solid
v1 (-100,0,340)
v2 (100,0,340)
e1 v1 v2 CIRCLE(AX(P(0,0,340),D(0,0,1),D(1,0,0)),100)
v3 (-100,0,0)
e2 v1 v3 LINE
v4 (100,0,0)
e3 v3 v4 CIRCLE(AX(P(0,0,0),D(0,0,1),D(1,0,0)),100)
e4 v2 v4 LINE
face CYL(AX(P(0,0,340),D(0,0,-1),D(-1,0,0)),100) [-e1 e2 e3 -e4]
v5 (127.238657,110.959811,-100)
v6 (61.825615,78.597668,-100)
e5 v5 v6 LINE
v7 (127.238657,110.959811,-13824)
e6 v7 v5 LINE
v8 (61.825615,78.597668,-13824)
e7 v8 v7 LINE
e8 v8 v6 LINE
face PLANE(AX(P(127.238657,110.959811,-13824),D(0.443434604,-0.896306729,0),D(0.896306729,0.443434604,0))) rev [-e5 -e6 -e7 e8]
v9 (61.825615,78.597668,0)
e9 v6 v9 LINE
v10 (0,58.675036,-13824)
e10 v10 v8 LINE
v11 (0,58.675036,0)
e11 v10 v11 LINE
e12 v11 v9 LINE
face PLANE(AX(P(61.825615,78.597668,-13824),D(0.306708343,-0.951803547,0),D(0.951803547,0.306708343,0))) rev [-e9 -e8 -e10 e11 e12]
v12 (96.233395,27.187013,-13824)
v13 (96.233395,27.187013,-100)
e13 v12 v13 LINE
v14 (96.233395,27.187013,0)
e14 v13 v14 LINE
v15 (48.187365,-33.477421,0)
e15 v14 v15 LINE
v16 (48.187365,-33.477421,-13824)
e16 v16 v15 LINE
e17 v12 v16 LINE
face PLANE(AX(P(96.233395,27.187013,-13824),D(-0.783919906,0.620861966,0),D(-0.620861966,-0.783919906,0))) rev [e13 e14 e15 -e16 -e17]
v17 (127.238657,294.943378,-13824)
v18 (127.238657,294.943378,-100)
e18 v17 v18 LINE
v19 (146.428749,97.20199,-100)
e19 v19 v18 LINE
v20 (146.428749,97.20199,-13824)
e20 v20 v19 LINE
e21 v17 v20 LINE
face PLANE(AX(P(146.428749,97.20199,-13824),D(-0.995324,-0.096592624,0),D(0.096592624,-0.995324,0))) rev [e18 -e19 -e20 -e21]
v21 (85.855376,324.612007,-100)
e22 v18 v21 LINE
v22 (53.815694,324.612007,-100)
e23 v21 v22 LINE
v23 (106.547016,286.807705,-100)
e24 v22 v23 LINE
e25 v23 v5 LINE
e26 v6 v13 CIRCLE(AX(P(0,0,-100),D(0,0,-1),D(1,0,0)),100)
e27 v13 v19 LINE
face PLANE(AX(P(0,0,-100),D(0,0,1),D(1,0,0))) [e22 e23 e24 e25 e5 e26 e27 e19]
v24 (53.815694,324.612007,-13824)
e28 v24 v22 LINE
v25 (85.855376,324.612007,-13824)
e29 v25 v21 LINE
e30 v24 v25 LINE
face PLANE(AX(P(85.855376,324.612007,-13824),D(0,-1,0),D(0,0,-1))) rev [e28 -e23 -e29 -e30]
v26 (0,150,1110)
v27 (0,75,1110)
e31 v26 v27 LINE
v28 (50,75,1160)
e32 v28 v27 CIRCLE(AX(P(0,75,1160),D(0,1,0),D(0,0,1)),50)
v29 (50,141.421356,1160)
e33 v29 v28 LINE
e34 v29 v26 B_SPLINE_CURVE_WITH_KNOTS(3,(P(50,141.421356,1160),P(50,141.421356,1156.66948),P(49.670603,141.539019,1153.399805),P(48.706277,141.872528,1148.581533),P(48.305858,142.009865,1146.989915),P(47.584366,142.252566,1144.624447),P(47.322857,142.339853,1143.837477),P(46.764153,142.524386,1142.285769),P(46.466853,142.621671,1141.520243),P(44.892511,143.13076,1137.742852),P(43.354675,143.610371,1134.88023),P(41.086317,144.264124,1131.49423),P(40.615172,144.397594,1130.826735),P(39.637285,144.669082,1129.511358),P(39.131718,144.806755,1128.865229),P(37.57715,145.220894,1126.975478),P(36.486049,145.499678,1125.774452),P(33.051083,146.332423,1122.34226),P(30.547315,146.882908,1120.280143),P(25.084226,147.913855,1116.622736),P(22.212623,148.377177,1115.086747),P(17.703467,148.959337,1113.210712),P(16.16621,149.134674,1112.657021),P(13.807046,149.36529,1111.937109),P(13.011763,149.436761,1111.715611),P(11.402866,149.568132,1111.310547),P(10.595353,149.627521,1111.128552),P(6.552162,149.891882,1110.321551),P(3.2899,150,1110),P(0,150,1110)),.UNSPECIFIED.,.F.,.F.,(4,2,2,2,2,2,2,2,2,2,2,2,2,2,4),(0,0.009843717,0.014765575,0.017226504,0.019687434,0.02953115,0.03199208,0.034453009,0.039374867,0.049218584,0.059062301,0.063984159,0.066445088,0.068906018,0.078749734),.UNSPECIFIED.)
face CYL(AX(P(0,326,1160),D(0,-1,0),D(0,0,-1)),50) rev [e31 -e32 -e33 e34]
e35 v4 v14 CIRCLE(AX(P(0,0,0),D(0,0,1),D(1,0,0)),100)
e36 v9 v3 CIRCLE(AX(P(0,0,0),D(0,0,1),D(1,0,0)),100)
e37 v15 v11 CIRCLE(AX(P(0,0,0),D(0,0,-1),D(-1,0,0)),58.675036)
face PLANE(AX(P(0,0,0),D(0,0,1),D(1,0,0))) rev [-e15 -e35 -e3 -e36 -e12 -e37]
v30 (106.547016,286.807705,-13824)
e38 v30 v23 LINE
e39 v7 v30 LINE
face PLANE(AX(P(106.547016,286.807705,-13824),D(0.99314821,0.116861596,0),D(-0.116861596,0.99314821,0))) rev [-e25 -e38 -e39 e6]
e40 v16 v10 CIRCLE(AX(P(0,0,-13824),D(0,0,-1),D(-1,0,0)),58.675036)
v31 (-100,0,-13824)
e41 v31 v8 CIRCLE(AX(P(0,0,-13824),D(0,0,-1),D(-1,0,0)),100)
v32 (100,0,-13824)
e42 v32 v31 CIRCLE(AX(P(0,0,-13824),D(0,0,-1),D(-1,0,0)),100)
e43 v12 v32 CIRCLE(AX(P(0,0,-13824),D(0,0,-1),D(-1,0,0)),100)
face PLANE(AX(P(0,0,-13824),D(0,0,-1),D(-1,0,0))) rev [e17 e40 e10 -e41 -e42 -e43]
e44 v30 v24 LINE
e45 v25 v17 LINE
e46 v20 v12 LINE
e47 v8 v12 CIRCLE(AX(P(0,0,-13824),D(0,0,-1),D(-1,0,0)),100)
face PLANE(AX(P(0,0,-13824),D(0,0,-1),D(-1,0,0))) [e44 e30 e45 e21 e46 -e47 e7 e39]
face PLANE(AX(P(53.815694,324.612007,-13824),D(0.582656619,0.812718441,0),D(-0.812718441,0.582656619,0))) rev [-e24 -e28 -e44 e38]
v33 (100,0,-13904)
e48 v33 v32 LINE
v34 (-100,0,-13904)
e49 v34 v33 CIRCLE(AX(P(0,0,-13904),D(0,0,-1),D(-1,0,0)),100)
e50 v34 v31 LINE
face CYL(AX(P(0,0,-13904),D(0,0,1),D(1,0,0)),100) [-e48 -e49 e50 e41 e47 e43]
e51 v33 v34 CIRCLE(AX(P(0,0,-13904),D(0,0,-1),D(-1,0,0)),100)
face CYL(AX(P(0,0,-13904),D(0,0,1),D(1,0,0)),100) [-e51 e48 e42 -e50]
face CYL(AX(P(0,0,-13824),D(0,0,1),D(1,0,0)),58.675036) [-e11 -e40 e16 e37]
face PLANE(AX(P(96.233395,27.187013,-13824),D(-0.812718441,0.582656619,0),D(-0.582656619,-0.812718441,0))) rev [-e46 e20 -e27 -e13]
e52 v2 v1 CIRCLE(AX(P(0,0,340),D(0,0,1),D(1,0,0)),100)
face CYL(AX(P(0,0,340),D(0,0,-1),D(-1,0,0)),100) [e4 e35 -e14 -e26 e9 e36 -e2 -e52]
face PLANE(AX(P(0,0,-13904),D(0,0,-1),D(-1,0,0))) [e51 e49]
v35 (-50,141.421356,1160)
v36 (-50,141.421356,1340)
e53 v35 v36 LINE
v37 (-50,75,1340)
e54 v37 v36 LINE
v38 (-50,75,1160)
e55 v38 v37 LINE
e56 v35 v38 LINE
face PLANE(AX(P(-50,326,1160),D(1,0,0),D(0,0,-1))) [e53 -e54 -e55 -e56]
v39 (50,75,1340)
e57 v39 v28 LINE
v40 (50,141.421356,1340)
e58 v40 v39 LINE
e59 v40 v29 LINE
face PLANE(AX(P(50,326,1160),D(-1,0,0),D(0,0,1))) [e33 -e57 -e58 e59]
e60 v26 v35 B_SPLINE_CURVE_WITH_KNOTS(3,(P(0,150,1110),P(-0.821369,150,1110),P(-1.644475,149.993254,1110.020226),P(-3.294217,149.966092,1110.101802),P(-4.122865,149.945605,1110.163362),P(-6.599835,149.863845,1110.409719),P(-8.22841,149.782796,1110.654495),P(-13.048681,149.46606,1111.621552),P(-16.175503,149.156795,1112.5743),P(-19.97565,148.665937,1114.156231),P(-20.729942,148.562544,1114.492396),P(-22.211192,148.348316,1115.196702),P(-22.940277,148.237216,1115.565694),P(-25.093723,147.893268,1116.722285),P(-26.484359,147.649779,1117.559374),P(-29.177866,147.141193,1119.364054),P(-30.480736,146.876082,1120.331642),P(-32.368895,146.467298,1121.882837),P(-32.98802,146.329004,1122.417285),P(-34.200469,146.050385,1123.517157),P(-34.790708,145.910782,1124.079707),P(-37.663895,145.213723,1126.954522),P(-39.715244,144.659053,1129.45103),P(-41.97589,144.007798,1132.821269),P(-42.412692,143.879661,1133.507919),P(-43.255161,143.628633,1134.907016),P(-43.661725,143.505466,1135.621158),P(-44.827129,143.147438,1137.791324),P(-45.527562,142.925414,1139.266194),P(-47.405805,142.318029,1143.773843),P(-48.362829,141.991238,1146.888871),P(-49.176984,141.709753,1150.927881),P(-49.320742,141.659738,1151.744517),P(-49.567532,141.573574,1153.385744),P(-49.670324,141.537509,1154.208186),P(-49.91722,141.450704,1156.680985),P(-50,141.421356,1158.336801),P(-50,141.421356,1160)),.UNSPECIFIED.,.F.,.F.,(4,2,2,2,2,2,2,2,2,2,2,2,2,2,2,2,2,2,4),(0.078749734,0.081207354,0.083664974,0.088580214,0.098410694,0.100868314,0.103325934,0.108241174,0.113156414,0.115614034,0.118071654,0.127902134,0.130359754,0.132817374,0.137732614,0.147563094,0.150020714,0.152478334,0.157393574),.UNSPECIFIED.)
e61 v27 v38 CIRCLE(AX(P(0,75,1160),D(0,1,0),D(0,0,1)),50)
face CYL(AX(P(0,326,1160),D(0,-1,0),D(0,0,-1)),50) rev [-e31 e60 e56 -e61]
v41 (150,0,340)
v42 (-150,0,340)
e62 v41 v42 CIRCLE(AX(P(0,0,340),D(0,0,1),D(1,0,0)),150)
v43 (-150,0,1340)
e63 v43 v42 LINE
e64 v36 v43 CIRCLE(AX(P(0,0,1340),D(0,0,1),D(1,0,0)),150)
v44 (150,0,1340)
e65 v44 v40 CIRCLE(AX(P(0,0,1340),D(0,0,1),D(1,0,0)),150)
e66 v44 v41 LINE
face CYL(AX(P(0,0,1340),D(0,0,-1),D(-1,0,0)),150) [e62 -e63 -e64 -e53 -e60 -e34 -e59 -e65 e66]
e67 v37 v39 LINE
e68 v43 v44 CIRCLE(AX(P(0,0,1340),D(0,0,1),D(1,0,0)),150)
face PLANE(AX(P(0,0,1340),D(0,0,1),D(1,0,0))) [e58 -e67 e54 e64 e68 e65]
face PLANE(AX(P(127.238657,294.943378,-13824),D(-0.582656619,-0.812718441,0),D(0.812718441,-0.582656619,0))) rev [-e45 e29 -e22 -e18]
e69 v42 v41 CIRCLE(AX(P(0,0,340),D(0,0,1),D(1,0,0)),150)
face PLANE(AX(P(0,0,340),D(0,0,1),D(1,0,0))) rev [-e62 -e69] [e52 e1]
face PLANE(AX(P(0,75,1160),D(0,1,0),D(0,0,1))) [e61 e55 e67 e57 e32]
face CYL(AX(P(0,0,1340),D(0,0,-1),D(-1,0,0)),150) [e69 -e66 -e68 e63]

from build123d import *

# Parameters (mm, degrees)
SKETCH1_R           = 100
BOSS_EXTRUDE1_DEPTH = 340
BOSS_EXTRUDE2_DEPTH = 13824
BOSS_EXTRUDE3_START = 80
SKETCH3_R           = 100
BOSS_EXTRUDE3_DEPTH = 80
CUT_EXTRUDE1_START  = -100
CUT_EXTRUDE1_DEPTH  = 100
SKETCH6_R           = 150
BOSS_EXTRUDE5_DEPTH = 1000
CUT_EXTRUDE2_DEPTH  = 326
BOSS_EXTRUDE6_DEPTH = 75


with BuildPart() as part:
    # Sketch1 → Boss-Extrude1 (new body)
    with BuildSketch(Plane.XY):
        Circle(SKETCH1_R)
    extrude(amount=BOSS_EXTRUDE1_DEPTH)

    # Sketch2 → Boss-Extrude2 (add)
    with BuildSketch(Plane(origin=(0, 0, 0), x_dir=(-1, 0, 0), z_dir=(0, 0, -1))):
        with BuildLine():
            Line((-96.233395069, 27.187012957), (-146.428749083, 97.201990132))
            Line((-146.428749083, 97.201990132), (-127.238656611, 294.943377783))
            Line((-127.238656611, 294.943377783), (-85.855376139, 324.612007229))
            Line((-85.855376139, 324.612007229), (-53.815694107, 324.612007229))
            Line((-53.815694107, 324.612007229), (-69.835535123, 313.127013254))
            Line((-69.835535123, 313.127013254), (-106.547016375, 286.807704556))
            Line((-106.547016375, 286.807704556), (-127.238656611, 110.959810588))
            Line((-127.238656611, 110.959810588), (-61.825614615, 78.597667761))
            Line((-61.825614615, 78.597667761), (0, 58.675035722))
            ThreePointArc((0, 58.675035722), (51.995426196, -27.188885075), (-48.18736452, -33.477421012))
            Line((-48.18736452, -33.477421012), (-96.233395069, 27.187012957))
        make_face()
    extrude(amount=BOSS_EXTRUDE2_DEPTH)

    # Sketch3 → Boss-Extrude3 (add)
    with BuildSketch(Plane(origin=(0, 0, -13824), x_dir=(-1, 0, 0), z_dir=(0, 0, -1)).offset(BOSS_EXTRUDE3_START)):
        with Locations(Location((0, 0, 0), (0, 0, 128.188900559))):
            Circle(SKETCH3_R)
    extrude(amount=-BOSS_EXTRUDE3_DEPTH)

    # Sketch4 → Cut-Extrude1 (cut)
    with BuildSketch(Plane.XY.offset(CUT_EXTRUDE1_START)):
        with BuildLine():
            Line((96.233395069, 27.187012957), (146.428749083, 97.201990132))
            Line((146.428749083, 97.201990132), (127.238656611, 294.943377783))
            Line((127.238656611, 294.943377783), (85.855376139, 324.612007229))
            Line((85.855376139, 324.612007229), (53.815694107, 324.612007229))
            Line((53.815694107, 324.612007229), (106.547016375, 286.807704556))
            Line((106.547016375, 286.807704556), (127.238656611, 110.959810588))
            Line((127.238656611, 110.959810588), (61.825614615, 78.597667761))
            ThreePointArc((61.825614615, 78.597667761), (83.104912565, 55.619902082), (96.233395069, 27.187012957))
        make_face()
    extrude(amount=CUT_EXTRUDE1_DEPTH, mode=Mode.SUBTRACT)

    # Sketch6 → Boss-Extrude5 (add)
    with BuildSketch(Plane.XY.offset(340)):
        Circle(SKETCH6_R)
    extrude(amount=BOSS_EXTRUDE5_DEPTH)

    # Sketch7 → Cut-Extrude2 (cut)
    with BuildSketch(Plane(origin=(0, 0, 0), x_dir=(1, 0, 0), z_dir=(0, 1, 0))):
        with BuildLine():
            Line((50, -1160), (50, -1460))
            ThreePointArc((50, -1460), (0, -1510), (-50, -1460))
            Line((-50, -1460), (-50, -1160))
            ThreePointArc((-50, -1160), (0, -1110), (50, -1160))
        make_face()
    extrude(amount=CUT_EXTRUDE2_DEPTH, mode=Mode.SUBTRACT)

    # Sketch8 → Boss-Extrude6 (add)
    with BuildSketch(Plane(origin=(0, 0, 0), x_dir=(1, 0, 0), z_dir=(0, 1, 0))):
        with BuildLine():
            Line((-50, -1160), (-50, -1340))
            Line((-50, -1340), (50, -1340))
            Line((50, -1340), (50, -1160))
            ThreePointArc((50, -1160), (0, -1110), (-50, -1160))
        make_face()
    extrude(amount=BOSS_EXTRUDE6_DEPTH)


solid = part.part
